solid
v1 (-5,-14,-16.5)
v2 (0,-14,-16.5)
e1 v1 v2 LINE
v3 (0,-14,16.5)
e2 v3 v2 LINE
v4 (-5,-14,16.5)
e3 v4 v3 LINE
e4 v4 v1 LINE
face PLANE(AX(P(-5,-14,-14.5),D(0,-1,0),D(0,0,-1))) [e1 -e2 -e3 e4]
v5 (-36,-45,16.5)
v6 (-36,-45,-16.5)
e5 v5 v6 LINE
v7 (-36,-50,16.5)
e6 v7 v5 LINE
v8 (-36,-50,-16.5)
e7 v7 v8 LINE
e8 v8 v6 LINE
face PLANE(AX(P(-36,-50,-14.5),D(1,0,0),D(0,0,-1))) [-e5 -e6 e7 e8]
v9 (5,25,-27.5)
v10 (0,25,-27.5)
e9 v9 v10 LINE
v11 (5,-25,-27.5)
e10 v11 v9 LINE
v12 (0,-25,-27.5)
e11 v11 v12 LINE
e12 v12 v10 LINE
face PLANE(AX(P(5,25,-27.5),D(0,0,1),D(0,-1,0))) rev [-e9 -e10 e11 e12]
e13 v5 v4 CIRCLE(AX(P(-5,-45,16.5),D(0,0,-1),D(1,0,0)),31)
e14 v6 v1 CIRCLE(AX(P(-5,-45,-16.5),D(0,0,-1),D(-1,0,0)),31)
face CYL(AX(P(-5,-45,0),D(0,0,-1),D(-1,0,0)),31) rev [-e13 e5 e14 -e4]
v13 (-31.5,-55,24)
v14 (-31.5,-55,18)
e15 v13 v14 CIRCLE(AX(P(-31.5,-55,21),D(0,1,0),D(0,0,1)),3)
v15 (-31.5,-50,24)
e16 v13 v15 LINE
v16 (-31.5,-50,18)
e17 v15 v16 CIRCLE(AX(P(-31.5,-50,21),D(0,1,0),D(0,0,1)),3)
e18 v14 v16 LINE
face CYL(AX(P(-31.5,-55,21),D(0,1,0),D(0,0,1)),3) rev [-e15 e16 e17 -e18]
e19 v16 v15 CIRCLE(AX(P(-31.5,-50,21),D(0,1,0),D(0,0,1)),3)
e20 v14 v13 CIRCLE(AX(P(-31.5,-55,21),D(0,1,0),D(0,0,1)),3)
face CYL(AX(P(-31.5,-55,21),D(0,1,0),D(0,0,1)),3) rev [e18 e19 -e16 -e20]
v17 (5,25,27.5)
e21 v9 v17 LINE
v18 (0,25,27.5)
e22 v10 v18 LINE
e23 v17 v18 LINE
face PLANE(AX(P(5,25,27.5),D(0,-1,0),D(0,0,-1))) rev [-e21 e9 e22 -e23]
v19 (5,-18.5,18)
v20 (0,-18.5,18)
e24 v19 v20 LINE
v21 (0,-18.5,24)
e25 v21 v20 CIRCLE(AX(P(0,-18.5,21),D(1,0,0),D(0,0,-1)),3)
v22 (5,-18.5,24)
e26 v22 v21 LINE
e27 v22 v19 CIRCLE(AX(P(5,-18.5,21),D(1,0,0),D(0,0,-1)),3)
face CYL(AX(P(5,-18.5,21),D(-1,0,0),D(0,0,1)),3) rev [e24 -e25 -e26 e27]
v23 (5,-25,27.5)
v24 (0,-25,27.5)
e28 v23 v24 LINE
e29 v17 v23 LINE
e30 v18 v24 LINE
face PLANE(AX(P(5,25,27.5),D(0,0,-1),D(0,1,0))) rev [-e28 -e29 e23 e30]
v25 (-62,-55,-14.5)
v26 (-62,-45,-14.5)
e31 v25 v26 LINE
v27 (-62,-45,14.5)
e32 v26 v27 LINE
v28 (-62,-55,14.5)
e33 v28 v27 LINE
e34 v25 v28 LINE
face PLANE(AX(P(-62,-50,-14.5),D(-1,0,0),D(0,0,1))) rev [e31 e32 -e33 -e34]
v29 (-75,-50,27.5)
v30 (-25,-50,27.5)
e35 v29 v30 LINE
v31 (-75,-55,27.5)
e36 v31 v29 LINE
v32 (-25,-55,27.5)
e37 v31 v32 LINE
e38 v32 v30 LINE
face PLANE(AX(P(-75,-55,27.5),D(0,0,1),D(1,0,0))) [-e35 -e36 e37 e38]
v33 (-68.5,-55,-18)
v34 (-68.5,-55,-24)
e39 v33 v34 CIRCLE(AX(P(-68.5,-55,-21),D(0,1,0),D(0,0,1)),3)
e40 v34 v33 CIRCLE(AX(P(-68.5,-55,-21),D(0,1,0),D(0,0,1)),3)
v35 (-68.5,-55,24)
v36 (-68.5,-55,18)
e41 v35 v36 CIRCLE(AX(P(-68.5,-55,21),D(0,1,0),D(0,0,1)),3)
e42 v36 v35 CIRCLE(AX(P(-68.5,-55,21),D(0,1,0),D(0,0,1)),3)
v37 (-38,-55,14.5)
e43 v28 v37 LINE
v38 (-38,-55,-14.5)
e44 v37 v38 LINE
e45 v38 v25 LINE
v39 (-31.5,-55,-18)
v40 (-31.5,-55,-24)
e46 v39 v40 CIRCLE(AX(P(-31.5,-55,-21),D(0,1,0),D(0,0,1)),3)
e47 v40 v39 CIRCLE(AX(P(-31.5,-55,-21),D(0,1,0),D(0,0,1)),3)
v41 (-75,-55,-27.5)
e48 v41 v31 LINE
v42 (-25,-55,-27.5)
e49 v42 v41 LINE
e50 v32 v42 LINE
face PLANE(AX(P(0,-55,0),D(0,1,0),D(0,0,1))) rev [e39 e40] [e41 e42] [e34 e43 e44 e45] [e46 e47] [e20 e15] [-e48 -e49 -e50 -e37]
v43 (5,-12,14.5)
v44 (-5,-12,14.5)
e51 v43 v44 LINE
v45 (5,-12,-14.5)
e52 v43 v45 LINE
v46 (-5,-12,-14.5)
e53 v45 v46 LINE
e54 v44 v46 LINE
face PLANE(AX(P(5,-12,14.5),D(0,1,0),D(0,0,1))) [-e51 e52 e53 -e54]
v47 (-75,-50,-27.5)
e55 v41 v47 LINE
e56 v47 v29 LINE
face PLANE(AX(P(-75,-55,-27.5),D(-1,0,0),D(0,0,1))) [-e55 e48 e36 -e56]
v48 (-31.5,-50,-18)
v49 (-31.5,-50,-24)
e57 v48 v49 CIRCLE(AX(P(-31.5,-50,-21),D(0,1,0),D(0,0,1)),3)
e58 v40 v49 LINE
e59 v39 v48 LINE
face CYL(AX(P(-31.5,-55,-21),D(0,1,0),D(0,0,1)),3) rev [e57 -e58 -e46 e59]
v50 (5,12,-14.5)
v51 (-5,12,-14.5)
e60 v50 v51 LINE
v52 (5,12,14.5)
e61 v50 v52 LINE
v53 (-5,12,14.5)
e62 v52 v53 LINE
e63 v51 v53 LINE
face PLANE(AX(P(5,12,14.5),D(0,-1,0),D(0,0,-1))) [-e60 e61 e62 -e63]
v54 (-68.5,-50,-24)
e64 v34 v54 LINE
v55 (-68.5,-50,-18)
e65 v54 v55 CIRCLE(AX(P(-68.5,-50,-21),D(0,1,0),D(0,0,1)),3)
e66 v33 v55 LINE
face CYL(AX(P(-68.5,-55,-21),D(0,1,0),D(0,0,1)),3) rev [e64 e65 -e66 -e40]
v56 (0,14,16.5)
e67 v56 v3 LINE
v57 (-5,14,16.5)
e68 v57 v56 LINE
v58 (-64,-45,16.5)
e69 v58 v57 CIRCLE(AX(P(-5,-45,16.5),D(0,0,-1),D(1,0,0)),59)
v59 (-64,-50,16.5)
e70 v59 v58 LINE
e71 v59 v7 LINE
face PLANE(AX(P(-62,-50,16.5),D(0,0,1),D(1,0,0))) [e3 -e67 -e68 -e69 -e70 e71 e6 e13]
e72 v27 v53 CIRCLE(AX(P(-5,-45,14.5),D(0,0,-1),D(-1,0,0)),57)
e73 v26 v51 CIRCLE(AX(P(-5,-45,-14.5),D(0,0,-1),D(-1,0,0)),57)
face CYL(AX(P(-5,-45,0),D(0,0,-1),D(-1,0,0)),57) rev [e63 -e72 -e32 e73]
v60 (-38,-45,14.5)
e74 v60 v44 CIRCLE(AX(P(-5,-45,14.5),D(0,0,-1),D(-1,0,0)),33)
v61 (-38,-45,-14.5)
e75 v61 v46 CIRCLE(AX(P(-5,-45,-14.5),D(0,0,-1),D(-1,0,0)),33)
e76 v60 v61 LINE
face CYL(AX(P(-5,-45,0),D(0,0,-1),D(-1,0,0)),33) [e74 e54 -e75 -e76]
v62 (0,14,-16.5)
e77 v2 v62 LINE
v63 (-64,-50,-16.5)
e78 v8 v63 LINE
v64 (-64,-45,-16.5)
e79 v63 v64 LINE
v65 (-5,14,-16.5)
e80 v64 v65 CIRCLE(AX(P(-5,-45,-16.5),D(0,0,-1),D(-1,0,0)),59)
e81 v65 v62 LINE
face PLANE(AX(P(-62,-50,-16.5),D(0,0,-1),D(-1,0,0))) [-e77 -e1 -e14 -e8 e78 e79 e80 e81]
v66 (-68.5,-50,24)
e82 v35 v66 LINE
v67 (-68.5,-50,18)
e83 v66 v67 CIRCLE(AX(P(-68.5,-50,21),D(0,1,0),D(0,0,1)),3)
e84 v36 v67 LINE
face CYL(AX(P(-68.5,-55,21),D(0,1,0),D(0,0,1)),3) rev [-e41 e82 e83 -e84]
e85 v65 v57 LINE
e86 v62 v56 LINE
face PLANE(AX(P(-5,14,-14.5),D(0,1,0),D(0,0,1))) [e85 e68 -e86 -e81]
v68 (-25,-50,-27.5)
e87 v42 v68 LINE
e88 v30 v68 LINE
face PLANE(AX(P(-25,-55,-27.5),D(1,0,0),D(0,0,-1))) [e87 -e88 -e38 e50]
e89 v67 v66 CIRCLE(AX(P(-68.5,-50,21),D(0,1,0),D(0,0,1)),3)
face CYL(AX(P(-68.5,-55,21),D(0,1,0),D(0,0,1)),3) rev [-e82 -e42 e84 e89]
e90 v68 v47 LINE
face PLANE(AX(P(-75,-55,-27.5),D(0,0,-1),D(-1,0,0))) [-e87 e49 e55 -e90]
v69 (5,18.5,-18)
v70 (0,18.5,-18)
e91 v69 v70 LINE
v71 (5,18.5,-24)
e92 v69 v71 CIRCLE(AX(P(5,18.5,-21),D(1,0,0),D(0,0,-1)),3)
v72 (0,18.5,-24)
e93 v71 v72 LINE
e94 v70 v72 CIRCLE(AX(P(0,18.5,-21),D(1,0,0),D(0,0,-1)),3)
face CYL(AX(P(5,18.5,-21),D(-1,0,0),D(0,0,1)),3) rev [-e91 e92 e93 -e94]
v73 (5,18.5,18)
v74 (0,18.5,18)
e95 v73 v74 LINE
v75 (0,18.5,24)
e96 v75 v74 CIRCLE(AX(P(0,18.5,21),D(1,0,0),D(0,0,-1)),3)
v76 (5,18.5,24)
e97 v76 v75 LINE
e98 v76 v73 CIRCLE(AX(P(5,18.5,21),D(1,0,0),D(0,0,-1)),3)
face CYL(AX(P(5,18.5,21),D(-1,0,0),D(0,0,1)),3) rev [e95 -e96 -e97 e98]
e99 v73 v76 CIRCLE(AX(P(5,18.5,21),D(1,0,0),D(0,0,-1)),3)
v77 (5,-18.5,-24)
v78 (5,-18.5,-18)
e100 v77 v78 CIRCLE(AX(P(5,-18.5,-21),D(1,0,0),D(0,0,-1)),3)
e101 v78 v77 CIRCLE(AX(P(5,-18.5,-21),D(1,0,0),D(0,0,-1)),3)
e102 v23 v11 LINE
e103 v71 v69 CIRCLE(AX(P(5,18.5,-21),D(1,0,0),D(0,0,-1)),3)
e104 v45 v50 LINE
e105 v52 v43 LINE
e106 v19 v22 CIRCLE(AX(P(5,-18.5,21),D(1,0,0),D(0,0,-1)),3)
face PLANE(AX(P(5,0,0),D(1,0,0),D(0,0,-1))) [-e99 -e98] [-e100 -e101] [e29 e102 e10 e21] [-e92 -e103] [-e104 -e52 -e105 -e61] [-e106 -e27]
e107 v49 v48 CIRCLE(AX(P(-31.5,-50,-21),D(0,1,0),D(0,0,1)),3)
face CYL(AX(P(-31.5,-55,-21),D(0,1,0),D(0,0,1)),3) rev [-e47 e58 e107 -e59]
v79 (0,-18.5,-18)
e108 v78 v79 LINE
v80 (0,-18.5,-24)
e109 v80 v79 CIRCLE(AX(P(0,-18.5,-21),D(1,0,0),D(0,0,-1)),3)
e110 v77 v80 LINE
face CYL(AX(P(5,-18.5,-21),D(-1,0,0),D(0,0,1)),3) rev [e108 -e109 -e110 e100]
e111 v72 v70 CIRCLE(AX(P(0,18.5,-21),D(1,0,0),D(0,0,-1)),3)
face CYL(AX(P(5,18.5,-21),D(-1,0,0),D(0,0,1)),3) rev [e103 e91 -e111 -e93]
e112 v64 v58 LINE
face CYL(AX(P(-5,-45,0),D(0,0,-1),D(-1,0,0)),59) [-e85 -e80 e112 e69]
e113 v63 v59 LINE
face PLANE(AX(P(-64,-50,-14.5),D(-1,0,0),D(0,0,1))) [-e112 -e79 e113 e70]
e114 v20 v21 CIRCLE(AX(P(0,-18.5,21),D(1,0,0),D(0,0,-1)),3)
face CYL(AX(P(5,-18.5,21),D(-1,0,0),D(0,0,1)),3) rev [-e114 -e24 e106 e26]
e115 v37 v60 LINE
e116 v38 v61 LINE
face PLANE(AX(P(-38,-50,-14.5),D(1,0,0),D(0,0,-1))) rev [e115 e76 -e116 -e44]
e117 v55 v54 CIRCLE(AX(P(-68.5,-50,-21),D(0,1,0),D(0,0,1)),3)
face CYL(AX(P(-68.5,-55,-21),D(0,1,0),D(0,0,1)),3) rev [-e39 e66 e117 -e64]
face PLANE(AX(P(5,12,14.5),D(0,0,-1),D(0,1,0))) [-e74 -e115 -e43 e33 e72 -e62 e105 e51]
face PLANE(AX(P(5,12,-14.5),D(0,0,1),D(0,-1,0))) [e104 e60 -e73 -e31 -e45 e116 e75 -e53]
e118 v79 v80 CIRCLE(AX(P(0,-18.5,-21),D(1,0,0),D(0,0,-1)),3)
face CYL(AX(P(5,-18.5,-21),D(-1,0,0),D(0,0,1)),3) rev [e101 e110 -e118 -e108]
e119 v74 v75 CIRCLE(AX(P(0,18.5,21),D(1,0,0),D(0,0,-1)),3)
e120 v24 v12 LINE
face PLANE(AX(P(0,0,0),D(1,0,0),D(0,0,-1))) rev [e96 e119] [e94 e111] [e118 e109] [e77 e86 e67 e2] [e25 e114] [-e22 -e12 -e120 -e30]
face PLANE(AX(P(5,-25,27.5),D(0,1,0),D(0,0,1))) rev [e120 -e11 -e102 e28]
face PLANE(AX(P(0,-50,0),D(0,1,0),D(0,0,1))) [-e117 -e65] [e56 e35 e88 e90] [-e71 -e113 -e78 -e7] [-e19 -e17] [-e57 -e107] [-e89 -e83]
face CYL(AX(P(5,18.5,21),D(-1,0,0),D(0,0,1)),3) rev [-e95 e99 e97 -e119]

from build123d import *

# Parameters (mm, degrees)
INLET_FLANGE_SKETCH_W    = 55
INLET_FLANGE_SKETCH_H    = 50
INLET_FLANGE_SKETCH_R    = 3
INLET_FLANGE_SKETCH_W_2  = 29
INLET_FLANGE_SKETCH_H_2  = 24
INLET_FLANGE_5MM_DEPTH   = 5
OUTLET_FLANGE_SKETCH_W   = 50
OUTLET_FLANGE_SKETCH_H   = 55
OUTLET_FLANGE_SKETCH_R   = 3
OUTLET_FLANGE_SKETCH_W_2 = 24
OUTLET_FLANGE_SKETCH_H_2 = 29
OUTLET_FLANGE_5MM_DEPTH  = 5
BEND_PROFILE_SKETCH_W    = 28
BEND_PROFILE_SKETCH_H    = 33
BEND_PROFILE_SKETCH_W_2  = 24
BEND_PROFILE_SKETCH_H_2  = 29


with BuildPart() as part:
    # Inlet Flange Sketch → Inlet Flange 5mm (new body)
    with BuildSketch(Plane(origin=(0, 0, 0), x_dir=(0, 0, -1), z_dir=(1, 0, 0))):
        Rectangle(INLET_FLANGE_SKETCH_W, INLET_FLANGE_SKETCH_H)
        with Locations((-21, 18.5)):
            Circle(INLET_FLANGE_SKETCH_R, mode=Mode.SUBTRACT)
        with Locations((21, 18.5)):
            Circle(INLET_FLANGE_SKETCH_R, mode=Mode.SUBTRACT)
        with Locations((21, -18.5)):
            Circle(INLET_FLANGE_SKETCH_R, mode=Mode.SUBTRACT)
        with Locations((-21, -18.5)):
            Circle(INLET_FLANGE_SKETCH_R, mode=Mode.SUBTRACT)
        Rectangle(INLET_FLANGE_SKETCH_W_2, INLET_FLANGE_SKETCH_H_2, mode=Mode.SUBTRACT)
    extrude(amount=INLET_FLANGE_5MM_DEPTH)



with BuildPart() as body_2:
    # Outlet Flange Sketch → Outlet Flange 5mm (new body)
    with BuildSketch(Plane(origin=(0, -50, 0), x_dir=(1, 0, 0), z_dir=(0, 1, 0))):
        with Locations((-50, 0)):
            Rectangle(OUTLET_FLANGE_SKETCH_W, OUTLET_FLANGE_SKETCH_H)
        with Locations(Location((-68.5, 21, 0), (0, 0, 270))):
            Circle(OUTLET_FLANGE_SKETCH_R, mode=Mode.SUBTRACT)
        with Locations(Location((-31.5, 21, 0), (0, 0, 270))):
            Circle(OUTLET_FLANGE_SKETCH_R, mode=Mode.SUBTRACT)
        with Locations(Location((-31.5, -21, 0), (0, 0, 270))):
            Circle(OUTLET_FLANGE_SKETCH_R, mode=Mode.SUBTRACT)
        with Locations(Location((-68.5, -21, 0), (0, 0, 270))):
            Circle(OUTLET_FLANGE_SKETCH_R, mode=Mode.SUBTRACT)
        with Locations((-50, 0)):
            Rectangle(OUTLET_FLANGE_SKETCH_W_2, OUTLET_FLANGE_SKETCH_H_2, mode=Mode.SUBTRACT)
    extrude(amount=-OUTLET_FLANGE_5MM_DEPTH)


with BuildPart() as part_1:
    add(part.part)

    add(body_2.part)  # Elbow Bend Wall 2mm merges body 2
    # Elbow Bend Wall 2mm: sweep along a path in Bend Path R45 Sketch
    with BuildLine(Plane.XY) as elbow_bend_wall_2mm_path:
        Line((-50, -50), (-50, -45))
        ThreePointArc((-50, -45), (-36.819805153, -13.180194847), (-5, 0))
        Line((-5, 0), (0, 0))
    # Bend Profile Sketch → Elbow Bend Wall 2mm (sweep)
    with BuildSketch(Plane(origin=(0, -50, 0), x_dir=(1, 0, 0), z_dir=(0, 1, 0))):
        with Locations((-50, 0)):
            Rectangle(BEND_PROFILE_SKETCH_W, BEND_PROFILE_SKETCH_H)
        with Locations((-50, 0)):
            Rectangle(BEND_PROFILE_SKETCH_W_2, BEND_PROFILE_SKETCH_H_2, mode=Mode.SUBTRACT)
    sweep(path=elbow_bend_wall_2mm_path.line)


solid = part_1.part
